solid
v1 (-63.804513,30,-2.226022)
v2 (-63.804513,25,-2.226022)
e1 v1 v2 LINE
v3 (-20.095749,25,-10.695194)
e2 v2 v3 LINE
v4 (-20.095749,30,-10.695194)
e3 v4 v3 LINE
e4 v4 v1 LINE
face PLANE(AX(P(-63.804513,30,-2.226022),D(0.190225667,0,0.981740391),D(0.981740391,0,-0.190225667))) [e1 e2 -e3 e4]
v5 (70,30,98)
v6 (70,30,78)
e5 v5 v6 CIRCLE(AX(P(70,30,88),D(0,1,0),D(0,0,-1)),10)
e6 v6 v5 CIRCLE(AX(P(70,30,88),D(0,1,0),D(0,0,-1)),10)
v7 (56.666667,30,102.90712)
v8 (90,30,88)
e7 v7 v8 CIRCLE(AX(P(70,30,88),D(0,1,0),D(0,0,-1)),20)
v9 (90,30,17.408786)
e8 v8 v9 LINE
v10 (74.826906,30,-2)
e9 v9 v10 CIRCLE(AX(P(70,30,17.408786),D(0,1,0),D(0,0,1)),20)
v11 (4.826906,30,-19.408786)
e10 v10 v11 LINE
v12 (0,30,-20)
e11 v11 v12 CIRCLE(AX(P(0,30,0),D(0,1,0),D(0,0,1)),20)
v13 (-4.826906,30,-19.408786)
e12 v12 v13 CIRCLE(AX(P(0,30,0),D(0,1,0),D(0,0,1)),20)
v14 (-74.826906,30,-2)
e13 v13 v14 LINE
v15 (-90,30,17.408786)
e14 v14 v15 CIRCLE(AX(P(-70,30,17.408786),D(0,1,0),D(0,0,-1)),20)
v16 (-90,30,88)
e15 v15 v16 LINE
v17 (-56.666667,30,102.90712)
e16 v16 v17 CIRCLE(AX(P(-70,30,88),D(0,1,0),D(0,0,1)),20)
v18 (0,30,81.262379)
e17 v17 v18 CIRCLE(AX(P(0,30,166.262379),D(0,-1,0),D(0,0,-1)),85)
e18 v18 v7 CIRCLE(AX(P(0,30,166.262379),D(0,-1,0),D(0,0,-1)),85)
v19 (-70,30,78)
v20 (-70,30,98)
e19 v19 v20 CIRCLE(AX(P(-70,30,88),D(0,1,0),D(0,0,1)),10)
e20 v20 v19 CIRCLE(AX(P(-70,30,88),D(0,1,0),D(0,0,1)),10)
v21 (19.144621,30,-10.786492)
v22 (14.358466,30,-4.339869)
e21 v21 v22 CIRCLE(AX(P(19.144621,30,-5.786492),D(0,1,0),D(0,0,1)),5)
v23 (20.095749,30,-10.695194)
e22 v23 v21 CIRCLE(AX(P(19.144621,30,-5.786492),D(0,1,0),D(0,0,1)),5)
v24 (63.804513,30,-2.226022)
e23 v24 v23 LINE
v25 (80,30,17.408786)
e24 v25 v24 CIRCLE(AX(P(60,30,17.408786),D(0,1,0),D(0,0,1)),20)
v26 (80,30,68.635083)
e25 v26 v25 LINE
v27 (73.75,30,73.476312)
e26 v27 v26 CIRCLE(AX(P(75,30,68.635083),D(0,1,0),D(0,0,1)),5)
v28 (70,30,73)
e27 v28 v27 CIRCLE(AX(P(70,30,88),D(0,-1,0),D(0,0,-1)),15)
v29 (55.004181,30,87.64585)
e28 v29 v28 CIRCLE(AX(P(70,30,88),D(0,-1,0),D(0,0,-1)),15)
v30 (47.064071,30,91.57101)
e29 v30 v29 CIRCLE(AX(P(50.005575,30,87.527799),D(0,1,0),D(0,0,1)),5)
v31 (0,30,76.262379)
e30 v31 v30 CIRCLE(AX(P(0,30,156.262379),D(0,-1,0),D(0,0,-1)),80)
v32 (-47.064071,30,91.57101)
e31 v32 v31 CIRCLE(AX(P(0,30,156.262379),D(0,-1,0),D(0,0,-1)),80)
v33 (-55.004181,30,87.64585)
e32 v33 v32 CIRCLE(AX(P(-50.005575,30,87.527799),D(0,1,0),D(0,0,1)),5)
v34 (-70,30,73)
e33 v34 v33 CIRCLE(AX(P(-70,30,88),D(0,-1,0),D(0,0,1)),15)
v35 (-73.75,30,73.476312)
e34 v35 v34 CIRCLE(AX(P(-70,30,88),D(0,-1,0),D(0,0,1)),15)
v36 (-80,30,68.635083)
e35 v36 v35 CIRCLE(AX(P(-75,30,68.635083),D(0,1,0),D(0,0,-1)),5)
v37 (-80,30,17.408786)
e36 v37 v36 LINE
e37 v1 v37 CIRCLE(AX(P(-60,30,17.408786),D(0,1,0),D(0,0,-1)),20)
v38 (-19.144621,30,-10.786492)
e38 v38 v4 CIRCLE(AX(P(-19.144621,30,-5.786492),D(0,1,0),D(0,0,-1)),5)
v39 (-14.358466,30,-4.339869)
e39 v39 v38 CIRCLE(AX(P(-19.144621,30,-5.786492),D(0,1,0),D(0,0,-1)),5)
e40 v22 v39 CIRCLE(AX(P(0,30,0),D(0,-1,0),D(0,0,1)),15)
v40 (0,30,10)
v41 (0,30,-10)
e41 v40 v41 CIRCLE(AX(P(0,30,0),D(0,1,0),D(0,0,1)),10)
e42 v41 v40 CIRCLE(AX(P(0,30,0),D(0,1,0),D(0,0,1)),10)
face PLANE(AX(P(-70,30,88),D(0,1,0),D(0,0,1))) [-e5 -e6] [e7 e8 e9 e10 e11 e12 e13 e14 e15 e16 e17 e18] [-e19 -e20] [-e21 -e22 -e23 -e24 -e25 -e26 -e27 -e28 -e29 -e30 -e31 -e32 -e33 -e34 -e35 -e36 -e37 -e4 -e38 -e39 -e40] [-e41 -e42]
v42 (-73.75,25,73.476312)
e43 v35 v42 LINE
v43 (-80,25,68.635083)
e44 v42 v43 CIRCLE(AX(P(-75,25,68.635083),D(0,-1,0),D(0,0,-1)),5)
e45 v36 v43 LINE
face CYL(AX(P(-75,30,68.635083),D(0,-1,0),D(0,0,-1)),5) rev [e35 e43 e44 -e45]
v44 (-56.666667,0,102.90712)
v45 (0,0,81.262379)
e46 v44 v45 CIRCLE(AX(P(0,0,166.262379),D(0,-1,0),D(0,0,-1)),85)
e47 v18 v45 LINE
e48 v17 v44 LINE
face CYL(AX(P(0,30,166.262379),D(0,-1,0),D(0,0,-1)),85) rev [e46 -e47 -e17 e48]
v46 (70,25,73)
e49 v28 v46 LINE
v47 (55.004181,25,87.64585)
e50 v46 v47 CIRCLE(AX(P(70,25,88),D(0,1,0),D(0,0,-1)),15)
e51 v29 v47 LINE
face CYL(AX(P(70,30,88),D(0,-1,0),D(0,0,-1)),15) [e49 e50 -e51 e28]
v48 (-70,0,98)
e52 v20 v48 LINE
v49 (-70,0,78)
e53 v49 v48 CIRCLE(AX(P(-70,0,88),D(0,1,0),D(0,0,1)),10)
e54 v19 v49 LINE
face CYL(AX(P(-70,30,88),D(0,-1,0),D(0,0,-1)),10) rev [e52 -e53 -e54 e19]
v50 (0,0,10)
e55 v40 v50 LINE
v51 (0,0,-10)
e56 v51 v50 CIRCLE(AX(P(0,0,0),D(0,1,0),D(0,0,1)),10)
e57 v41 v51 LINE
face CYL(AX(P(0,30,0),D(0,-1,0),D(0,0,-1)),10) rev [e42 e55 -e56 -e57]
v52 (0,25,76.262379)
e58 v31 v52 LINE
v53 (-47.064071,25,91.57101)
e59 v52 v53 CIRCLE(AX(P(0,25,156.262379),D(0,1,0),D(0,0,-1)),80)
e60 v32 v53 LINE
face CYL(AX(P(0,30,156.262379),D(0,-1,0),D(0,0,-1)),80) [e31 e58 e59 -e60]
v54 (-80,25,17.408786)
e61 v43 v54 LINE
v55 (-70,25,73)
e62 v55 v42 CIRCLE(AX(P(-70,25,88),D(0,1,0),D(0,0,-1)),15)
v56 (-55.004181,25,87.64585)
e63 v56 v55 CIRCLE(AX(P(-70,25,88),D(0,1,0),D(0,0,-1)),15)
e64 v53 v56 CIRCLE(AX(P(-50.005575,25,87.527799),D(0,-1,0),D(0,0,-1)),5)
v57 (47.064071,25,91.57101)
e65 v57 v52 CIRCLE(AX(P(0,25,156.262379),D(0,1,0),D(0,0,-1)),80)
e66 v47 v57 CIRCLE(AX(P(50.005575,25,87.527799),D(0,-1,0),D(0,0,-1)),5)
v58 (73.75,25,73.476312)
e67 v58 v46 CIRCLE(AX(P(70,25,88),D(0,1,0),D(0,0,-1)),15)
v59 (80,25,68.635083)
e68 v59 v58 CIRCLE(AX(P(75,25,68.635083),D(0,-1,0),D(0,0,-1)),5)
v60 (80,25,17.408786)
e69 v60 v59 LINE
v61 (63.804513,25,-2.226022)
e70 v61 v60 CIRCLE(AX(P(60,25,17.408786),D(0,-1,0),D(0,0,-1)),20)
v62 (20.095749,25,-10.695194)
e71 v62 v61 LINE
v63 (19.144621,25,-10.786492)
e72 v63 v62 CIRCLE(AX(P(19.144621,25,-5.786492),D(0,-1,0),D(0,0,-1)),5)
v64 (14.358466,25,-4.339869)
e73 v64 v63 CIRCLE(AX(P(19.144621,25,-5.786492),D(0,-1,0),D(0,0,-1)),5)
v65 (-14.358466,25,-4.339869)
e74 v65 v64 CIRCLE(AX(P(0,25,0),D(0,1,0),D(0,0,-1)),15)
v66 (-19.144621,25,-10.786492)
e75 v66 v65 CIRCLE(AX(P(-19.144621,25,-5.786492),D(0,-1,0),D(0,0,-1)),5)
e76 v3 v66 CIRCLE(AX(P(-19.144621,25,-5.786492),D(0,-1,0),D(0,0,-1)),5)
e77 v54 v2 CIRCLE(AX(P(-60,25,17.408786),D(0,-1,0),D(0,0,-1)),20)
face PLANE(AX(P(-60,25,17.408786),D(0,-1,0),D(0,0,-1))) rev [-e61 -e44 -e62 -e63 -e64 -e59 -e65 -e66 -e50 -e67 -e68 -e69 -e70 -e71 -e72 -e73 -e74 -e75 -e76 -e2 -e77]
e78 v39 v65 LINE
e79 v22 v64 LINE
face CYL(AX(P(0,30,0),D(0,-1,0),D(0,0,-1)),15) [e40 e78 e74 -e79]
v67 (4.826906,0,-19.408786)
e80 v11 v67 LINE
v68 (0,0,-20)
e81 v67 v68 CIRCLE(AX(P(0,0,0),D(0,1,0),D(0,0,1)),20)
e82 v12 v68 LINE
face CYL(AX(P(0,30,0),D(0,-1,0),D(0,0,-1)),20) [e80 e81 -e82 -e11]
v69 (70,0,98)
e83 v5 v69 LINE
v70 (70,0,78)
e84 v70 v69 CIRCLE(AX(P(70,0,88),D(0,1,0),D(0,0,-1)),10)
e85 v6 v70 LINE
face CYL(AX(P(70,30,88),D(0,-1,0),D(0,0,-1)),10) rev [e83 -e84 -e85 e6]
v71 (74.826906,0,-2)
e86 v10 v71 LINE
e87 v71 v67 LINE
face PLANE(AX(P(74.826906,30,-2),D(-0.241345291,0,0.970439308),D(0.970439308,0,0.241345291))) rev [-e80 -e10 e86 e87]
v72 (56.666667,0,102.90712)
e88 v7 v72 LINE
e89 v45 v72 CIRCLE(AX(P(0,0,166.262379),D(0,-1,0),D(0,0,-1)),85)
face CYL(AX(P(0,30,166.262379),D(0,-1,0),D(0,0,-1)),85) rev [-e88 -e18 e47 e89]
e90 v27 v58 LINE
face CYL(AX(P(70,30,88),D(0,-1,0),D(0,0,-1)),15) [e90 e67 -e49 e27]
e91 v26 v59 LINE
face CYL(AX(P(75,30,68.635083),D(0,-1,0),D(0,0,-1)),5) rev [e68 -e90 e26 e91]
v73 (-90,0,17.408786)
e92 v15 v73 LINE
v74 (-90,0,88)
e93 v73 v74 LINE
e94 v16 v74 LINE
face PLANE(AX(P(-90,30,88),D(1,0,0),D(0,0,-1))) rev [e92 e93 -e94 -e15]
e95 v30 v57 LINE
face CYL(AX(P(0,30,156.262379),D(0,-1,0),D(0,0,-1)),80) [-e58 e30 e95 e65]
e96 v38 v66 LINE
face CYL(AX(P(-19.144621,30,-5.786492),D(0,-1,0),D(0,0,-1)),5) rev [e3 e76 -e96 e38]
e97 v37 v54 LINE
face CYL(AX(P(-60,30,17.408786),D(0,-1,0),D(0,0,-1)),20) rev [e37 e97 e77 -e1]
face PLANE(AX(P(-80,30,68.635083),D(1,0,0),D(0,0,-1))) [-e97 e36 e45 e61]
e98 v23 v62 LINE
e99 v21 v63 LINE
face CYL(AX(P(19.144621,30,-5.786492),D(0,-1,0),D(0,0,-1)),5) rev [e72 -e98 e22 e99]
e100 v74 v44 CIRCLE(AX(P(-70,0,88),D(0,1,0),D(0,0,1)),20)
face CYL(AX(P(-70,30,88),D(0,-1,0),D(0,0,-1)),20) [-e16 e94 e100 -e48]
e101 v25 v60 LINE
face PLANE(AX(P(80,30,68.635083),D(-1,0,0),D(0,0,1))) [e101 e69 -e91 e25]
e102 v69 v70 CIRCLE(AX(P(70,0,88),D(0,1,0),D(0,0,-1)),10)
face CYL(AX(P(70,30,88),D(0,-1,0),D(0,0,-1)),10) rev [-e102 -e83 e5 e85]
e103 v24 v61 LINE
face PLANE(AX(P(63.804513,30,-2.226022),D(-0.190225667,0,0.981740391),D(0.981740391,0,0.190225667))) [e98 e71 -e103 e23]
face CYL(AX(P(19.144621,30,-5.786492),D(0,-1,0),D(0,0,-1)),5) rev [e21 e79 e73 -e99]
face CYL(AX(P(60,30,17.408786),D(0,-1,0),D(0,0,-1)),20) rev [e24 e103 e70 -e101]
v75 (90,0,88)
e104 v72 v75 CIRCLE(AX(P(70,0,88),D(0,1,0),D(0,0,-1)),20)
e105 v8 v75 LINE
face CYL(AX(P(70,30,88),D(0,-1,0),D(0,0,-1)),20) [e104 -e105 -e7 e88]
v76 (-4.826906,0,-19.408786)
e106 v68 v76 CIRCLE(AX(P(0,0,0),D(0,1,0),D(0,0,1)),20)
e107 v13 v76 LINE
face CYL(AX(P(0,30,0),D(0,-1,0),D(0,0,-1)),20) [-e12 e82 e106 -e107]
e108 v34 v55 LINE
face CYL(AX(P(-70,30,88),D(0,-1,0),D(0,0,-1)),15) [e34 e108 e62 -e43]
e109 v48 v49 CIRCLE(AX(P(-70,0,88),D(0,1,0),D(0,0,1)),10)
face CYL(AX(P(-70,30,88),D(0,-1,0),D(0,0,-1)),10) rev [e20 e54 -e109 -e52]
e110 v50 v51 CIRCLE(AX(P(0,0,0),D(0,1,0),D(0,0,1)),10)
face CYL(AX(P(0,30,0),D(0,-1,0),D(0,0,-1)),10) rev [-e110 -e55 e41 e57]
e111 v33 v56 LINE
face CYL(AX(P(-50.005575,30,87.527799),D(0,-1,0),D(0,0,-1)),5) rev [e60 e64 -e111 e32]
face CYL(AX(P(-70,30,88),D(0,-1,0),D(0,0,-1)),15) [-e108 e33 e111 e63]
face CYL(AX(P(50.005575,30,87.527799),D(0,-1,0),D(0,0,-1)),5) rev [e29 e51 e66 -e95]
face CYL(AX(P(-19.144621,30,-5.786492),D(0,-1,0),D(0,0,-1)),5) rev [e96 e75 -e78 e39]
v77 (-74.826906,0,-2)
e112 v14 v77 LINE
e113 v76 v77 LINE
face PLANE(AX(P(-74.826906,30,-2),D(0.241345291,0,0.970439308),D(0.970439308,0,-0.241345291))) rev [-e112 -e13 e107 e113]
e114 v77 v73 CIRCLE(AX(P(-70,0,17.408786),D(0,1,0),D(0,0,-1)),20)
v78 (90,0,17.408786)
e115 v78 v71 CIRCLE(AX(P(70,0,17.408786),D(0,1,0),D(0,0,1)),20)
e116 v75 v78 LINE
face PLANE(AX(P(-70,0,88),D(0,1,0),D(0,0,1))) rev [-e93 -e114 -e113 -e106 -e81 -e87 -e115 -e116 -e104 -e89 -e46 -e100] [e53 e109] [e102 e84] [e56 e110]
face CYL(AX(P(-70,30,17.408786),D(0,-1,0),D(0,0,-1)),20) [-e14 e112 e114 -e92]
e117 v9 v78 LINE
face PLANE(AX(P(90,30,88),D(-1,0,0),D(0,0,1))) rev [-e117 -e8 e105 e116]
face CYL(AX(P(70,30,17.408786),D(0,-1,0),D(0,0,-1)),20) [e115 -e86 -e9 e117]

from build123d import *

# Parameters (mm, degrees)
PLATE_OUTLINE_SKETCH_R = 10
BASE_PLATE_30MM_DEPTH  = 30
TOP_POCKET_CUT_DEPTH   = 25


with BuildPart() as part:
    # Plate Outline Sketch → Base Plate 30mm (new body)
    with BuildSketch(Plane(origin=(0, 0, 0), x_dir=(1, 0, 0), z_dir=(0, 1, 0))):
        with BuildLine():
            Line((-90, -88), (-90, -17.408786158))
            ThreePointArc((-90, -17.408786158), (-85.756556041, -5.090874739), (-74.826905826, 2))
            Line((-74.826905826, 2), (-4.826905826, 19.408786158))
            ThreePointArc((-4.826905826, 19.408786158), (0, 20), (4.826905826, 19.408786158))
            Line((4.826905826, 19.408786158), (74.826905826, 2))
            ThreePointArc((74.826905826, 2), (85.756556041, -5.090874739), (90, -17.408786158))
            Line((90, -17.408786158), (90, -88))
            ThreePointArc((90, -88), (78.164965809, -106.257418584), (56.666666667, -102.90711985))
            ThreePointArc((56.666666667, -102.90711985), (0, -81.262379212), (-56.666666667, -102.90711985))
            ThreePointArc((-56.666666667, -102.90711985), (-78.164965809, -106.257418584), (-90, -88))
        make_face()
        with Locations(Location((0, 0, 0), (0, 0, 270))):
            Circle(PLATE_OUTLINE_SKETCH_R, mode=Mode.SUBTRACT)
        with Locations(Location((-70, -88, 0), (0, 0, 270))):
            Circle(PLATE_OUTLINE_SKETCH_R, mode=Mode.SUBTRACT)
        with Locations(Location((70, -88, 0), (0, 0, 90))):
            Circle(PLATE_OUTLINE_SKETCH_R, mode=Mode.SUBTRACT)
        with BuildLine():
            Line((-80, -68.635083269), (-80, -17.408786158))
            ThreePointArc((-80, -17.408786158), (-75.428711332, -4.682637227), (-63.804513336, 2.226021665))
            Line((-63.804513336, 2.226021665), (-20.095749168, 10.695194253))
            ThreePointArc((-20.095749168, 10.695194253), (-15.433233379, 9.136955423), (-14.358465626, 4.339869223))
            ThreePointArc((-14.358465626, 4.339869223), (0, -15), (14.358465626, 4.339869223))
            ThreePointArc((14.358465626, 4.339869223), (15.433233379, 9.136955423), (20.095749168, 10.695194253))
            Line((20.095749168, 10.695194253), (63.804513336, 2.226021665))
            ThreePointArc((63.804513336, 2.226021665), (75.428711332, -4.682637227), (80, -17.408786158))
            Line((80, -17.408786158), (80, -68.635083269))
            ThreePointArc((80, -68.635083269), (78.061862178, -72.587930344), (73.75, -73.476312452))
            ThreePointArc((73.75, -73.476312452), (60.955053625, -76.033841674), (55.004181334, -87.645849573))
            ThreePointArc((55.004181334, -87.645849573), (52.221345421, -92.010026772), (47.064070693, -91.571010006))
            ThreePointArc((47.064070693, -91.571010006), (0, -76.262379212), (-47.064070693, -91.571010006))
            ThreePointArc((-47.064070693, -91.571010006), (-52.221345421, -92.010026772), (-55.004181334, -87.645849573))
            ThreePointArc((-55.004181334, -87.645849573), (-60.955053625, -76.033841674), (-73.75, -73.476312452))
            ThreePointArc((-73.75, -73.476312452), (-78.061862178, -72.587930344), (-80, -68.635083269))
        make_face(mode=Mode.SUBTRACT)
    extrude(amount=BASE_PLATE_30MM_DEPTH)

    # Top Pocket Sketch → Top Pocket Cut (add)
    with BuildSketch(Plane.XZ):
        with BuildLine():
            Line((-20.095749168, -10.695194253), (-63.804513336, -2.226021665))
            ThreePointArc((-63.804513336, -2.226021665), (-75.428711332, 4.682637227), (-80, 17.408786158))
            Line((-80, 17.408786158), (-80, 68.635083269))
            ThreePointArc((-80, 68.635083269), (-78.061862178, 72.587930344), (-73.75, 73.476312452))
            ThreePointArc((-73.75, 73.476312452), (-60.955053625, 76.033841674), (-55.004181334, 87.645849573))
            ThreePointArc((-55.004181334, 87.645849573), (-52.221345421, 92.010026772), (-47.064070693, 91.571010006))
            ThreePointArc((-47.064070693, 91.571010006), (0, 76.262379212), (47.064070693, 91.571010006))
            ThreePointArc((47.064070693, 91.571010006), (52.221345421, 92.010026772), (55.004181334, 87.645849573))
            ThreePointArc((55.004181334, 87.645849573), (60.955053625, 76.033841674), (73.75, 73.476312452))
            ThreePointArc((73.75, 73.476312452), (78.061862178, 72.587930344), (80, 68.635083269))
            Line((80, 68.635083269), (80, 17.408786158))
            ThreePointArc((80, 17.408786158), (75.428711332, 4.682637227), (63.804513336, -2.226021665))
            Line((63.804513336, -2.226021665), (20.095749168, -10.695194253))
            ThreePointArc((20.095749168, -10.695194253), (15.433233379, -9.136955423), (14.358465626, -4.339869223))
            ThreePointArc((14.358465626, -4.339869223), (0, 15), (-14.358465626, -4.339869223))
            ThreePointArc((-14.358465626, -4.339869223), (-15.433233379, -9.136955423), (-20.095749168, -10.695194253))
        make_face()
    extrude(amount=-TOP_POCKET_CUT_DEPTH)


solid = part.part
